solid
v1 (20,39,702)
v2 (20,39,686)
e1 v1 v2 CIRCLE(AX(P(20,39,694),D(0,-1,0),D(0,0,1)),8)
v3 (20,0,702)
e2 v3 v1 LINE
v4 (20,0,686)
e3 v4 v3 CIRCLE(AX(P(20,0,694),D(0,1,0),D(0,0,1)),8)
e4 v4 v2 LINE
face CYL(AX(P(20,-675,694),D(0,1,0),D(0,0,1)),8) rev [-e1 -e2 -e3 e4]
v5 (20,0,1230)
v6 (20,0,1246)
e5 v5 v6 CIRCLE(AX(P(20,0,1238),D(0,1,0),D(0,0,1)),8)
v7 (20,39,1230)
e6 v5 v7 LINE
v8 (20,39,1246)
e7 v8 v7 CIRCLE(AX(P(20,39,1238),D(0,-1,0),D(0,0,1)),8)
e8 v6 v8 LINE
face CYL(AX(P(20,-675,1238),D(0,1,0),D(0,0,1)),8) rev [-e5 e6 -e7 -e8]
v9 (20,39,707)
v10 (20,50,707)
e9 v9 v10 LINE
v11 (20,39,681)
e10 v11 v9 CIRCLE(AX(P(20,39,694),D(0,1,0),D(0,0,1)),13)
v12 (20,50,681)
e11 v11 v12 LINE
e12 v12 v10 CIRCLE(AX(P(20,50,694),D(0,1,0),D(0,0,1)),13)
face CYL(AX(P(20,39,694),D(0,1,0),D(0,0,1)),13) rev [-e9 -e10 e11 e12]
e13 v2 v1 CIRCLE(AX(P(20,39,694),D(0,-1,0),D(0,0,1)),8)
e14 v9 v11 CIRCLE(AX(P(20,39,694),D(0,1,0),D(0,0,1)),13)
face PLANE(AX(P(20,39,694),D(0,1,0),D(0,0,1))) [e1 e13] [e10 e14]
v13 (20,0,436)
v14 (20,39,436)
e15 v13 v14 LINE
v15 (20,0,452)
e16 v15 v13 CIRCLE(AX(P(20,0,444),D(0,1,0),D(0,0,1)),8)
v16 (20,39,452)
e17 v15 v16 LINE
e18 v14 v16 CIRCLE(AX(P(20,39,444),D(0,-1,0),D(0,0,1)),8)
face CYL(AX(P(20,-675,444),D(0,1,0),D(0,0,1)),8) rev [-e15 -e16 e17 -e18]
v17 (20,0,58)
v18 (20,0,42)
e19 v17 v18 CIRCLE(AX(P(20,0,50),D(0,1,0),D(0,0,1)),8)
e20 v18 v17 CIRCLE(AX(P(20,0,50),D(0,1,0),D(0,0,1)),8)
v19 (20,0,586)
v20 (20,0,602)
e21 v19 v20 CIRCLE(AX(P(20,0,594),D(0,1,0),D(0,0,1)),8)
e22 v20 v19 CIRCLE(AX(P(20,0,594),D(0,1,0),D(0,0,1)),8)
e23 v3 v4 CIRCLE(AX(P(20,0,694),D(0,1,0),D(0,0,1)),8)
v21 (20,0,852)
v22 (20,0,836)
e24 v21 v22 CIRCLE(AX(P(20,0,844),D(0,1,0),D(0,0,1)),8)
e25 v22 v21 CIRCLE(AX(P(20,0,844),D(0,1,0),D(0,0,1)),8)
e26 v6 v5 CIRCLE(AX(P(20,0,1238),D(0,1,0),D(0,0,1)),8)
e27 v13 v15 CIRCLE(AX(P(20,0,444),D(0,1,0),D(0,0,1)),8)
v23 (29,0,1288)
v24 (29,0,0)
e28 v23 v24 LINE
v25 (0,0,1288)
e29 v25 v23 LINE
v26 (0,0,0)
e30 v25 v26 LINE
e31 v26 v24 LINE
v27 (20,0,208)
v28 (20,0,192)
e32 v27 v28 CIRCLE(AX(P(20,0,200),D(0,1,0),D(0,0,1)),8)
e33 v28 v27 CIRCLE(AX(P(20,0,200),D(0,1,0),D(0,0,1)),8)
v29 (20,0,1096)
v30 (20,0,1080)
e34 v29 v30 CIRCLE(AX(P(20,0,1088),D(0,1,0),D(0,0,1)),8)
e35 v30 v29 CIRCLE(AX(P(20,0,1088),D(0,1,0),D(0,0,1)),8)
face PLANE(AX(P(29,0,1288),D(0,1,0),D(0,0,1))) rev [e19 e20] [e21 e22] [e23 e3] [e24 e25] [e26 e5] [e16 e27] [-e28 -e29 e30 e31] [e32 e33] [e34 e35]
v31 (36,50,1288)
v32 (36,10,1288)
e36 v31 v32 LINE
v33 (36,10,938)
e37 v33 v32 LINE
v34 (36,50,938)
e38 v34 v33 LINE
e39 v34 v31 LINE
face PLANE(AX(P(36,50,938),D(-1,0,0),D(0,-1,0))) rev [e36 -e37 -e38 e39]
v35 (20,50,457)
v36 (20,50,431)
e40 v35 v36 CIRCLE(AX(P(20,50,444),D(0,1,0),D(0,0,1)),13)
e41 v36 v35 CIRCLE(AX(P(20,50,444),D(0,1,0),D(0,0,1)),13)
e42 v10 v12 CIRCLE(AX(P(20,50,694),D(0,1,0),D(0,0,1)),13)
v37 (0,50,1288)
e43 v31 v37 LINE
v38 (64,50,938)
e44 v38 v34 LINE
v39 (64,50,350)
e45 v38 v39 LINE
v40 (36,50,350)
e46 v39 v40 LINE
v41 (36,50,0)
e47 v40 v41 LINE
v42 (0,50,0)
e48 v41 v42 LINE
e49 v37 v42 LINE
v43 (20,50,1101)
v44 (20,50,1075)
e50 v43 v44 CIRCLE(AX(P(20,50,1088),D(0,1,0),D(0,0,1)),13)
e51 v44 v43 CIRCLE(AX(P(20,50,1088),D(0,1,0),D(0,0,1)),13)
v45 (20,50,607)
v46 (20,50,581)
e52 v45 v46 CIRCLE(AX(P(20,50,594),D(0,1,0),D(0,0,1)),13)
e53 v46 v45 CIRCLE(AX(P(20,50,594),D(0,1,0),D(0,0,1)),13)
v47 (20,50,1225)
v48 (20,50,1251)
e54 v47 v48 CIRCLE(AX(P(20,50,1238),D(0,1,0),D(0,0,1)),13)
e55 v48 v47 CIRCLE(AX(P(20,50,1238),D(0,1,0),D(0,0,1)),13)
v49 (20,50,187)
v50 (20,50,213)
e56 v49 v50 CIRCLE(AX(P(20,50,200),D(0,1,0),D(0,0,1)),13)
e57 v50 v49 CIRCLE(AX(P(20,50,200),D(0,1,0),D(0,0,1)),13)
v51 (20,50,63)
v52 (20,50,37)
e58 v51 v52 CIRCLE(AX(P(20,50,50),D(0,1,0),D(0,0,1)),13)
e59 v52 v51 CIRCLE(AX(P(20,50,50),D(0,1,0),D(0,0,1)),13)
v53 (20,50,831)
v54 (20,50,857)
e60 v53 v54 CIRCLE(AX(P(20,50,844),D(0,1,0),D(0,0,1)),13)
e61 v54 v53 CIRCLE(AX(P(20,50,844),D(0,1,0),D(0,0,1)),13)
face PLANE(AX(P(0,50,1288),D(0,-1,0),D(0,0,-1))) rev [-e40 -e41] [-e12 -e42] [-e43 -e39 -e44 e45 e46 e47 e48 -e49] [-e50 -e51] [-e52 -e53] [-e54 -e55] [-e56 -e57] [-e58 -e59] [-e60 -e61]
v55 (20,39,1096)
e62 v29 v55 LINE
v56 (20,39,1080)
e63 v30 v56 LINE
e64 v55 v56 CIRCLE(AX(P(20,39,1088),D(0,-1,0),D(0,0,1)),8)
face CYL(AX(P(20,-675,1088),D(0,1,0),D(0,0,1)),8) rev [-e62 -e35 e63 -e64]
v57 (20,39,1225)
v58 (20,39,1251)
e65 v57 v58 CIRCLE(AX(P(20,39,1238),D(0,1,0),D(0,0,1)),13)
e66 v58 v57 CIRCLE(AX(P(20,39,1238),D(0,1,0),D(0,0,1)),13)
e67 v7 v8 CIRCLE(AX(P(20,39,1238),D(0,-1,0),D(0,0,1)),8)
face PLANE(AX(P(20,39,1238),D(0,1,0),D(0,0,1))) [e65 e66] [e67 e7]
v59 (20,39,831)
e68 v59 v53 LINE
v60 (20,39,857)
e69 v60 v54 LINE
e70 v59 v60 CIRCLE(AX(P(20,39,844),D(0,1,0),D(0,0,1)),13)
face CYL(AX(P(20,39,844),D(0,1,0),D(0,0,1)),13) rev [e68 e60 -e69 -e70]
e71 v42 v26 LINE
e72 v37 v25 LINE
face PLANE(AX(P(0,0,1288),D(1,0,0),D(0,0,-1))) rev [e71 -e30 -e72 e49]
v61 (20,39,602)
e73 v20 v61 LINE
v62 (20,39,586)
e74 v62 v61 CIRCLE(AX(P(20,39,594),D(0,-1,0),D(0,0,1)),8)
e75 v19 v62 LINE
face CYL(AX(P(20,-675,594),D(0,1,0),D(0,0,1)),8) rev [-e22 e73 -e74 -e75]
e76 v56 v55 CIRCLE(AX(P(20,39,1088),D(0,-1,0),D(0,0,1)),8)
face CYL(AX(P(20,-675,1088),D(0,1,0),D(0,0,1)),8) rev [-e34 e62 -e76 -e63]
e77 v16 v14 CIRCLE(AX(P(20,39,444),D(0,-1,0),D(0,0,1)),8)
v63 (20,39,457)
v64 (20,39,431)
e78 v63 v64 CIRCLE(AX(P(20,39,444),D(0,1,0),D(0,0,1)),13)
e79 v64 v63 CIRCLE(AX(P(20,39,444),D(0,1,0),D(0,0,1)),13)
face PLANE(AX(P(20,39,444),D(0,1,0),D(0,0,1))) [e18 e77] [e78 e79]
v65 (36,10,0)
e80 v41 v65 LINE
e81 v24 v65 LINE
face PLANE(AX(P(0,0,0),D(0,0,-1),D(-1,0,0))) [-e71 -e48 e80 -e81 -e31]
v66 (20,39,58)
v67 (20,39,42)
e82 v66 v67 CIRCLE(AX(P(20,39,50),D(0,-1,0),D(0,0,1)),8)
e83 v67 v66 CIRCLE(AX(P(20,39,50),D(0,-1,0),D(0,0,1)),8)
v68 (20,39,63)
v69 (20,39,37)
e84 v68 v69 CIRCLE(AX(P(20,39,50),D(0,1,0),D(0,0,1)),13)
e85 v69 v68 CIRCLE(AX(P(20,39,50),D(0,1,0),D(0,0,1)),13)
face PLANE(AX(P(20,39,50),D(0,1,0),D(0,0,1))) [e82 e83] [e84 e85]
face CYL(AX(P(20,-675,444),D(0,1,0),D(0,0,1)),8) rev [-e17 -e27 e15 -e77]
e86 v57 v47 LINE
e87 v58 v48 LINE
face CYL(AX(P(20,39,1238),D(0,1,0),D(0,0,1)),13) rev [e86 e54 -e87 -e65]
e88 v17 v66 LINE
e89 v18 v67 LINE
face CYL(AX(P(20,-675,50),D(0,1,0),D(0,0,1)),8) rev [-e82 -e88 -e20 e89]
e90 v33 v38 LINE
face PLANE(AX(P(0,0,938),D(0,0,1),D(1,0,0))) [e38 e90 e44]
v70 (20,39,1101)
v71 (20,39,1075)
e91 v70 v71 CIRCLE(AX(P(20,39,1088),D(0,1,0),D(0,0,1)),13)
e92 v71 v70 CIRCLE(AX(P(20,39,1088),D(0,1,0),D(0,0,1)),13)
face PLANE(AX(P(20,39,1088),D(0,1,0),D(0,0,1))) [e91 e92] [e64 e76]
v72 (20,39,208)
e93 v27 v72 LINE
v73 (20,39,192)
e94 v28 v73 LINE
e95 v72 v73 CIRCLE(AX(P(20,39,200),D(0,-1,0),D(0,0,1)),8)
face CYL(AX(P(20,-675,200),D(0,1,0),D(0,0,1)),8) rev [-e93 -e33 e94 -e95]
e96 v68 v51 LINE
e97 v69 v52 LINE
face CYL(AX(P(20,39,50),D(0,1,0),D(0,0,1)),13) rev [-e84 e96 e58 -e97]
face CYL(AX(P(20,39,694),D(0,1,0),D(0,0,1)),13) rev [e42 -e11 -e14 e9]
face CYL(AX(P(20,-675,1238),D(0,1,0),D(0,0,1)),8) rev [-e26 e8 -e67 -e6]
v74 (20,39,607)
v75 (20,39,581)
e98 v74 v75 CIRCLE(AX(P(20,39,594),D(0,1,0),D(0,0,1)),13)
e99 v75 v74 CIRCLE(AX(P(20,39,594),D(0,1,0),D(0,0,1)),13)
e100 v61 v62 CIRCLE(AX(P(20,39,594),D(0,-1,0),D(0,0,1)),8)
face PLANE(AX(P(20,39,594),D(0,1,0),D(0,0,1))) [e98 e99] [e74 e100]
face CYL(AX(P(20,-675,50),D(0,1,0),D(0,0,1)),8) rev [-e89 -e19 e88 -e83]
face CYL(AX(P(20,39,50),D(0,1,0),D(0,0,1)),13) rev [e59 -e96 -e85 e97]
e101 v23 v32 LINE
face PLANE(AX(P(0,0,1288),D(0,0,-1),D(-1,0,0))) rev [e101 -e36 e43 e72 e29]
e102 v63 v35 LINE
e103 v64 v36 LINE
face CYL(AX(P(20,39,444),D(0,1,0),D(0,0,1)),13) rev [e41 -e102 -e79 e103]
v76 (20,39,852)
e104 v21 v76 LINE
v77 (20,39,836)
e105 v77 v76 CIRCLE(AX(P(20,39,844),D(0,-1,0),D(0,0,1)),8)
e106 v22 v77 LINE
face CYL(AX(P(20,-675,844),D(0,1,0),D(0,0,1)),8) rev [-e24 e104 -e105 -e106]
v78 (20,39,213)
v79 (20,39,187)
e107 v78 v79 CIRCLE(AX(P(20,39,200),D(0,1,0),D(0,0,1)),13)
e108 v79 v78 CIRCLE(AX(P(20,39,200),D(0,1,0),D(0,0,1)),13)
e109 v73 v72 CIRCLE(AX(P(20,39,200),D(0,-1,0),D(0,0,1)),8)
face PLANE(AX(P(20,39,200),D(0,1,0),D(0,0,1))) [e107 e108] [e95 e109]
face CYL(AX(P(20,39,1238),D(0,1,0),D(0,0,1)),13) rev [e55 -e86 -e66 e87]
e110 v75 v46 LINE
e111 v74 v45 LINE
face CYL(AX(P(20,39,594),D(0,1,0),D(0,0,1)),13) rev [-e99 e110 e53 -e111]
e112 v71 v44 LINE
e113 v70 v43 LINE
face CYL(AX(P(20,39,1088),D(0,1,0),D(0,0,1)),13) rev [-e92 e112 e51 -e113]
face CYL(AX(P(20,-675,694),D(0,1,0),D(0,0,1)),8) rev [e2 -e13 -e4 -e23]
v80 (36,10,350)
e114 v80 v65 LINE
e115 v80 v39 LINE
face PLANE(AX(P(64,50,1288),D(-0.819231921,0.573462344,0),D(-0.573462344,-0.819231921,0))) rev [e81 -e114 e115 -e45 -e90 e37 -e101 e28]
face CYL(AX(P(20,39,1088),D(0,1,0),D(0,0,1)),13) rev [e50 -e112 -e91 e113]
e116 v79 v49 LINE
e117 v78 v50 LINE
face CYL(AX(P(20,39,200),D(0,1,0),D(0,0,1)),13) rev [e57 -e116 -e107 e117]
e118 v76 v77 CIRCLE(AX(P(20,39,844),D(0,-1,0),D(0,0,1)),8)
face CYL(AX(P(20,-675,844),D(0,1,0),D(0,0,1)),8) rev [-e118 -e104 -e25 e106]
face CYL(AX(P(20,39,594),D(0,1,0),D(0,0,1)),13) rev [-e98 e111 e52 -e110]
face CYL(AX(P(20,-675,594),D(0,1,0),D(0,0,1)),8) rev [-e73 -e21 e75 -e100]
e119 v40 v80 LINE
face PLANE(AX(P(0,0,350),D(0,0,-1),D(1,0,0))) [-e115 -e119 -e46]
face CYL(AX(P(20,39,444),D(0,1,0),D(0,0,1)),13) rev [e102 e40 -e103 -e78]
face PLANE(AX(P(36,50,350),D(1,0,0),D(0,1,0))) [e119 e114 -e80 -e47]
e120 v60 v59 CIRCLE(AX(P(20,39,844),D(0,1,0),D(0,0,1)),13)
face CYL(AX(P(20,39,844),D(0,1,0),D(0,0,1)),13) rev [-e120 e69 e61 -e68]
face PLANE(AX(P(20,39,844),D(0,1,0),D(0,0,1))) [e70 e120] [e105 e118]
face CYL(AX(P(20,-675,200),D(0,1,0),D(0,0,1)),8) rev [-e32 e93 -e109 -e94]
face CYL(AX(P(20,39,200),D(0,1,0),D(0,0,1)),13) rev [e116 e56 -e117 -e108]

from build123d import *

# Parameters (mm, degrees)
EXTRUDE_1_DEPTH     = 1288
SKETCH_2_R          = 8
CUT_EXTRUDE_1_DEPTH = 725
SKETCH_3_R          = 13
CUT_EXTRUDE_2_DEPTH = 11
CUT_EXTRUDE_3_DEPTH = 350


with BuildPart() as part:
    # 草图1 → 凸台-拉伸1 (new body)
    with BuildSketch(Plane.XY):
        Polygon((0, 0), (0, 50), (64, 50), (29, 0), align=None)
    extrude(amount=EXTRUDE_1_DEPTH)

    # 草图2 → 切除-拉伸1 (cut)
    with BuildSketch(Plane(origin=(0, 50, 0), x_dir=(1, 0, 0), z_dir=(0, 1, 0))):
        with Locations(Location((20, -50, 0), (0, 0, 270))):
            Circle(SKETCH_2_R)
        with Locations(Location((20, -200, 0), (0, 0, 270))):
            Circle(SKETCH_2_R)
        with Locations(Location((20, -444, 0), (0, 0, 270))):
            Circle(SKETCH_2_R)
        with Locations(Location((20, -594, 0), (0, 0, 270))):
            Circle(SKETCH_2_R)
        with Locations(Location((20, -694, 0), (0, 0, 270))):
            Circle(SKETCH_2_R)
        with Locations(Location((20, -844, 0), (0, 0, 270))):
            Circle(SKETCH_2_R)
        with Locations(Location((20, -1088, 0), (0, 0, 270))):
            Circle(SKETCH_2_R)
        with Locations(Location((20, -1238, 0), (0, 0, 270))):
            Circle(SKETCH_2_R)
    extrude(amount=-CUT_EXTRUDE_1_DEPTH, mode=Mode.SUBTRACT)

    # 草图3 → 切除-拉伸2 (cut)
    with BuildSketch(Plane(origin=(0, 50, 0), x_dir=(1, 0, 0), z_dir=(0, 1, 0))):
        with Locations(Location((20, -50, 0), (0, 0, 270))):
            Circle(SKETCH_3_R)
        with Locations(Location((20, -200, 0), (0, 0, 270))):
            Circle(SKETCH_3_R)
        with Locations(Location((20, -444, 0), (0, 0, 270))):
            Circle(SKETCH_3_R)
        with Locations(Location((20, -594, 0), (0, 0, 270))):
            Circle(SKETCH_3_R)
        with Locations(Location((20, -694, 0), (0, 0, 270))):
            Circle(SKETCH_3_R)
        with Locations(Location((20, -844, 0), (0, 0, 270))):
            Circle(SKETCH_3_R)
        with Locations(Location((20, -1088, 0), (0, 0, 270))):
            Circle(SKETCH_3_R)
        with Locations(Location((20, -1238, 0), (0, 0, 270))):
            Circle(SKETCH_3_R)
    extrude(amount=-CUT_EXTRUDE_2_DEPTH, mode=Mode.SUBTRACT)

    # 草图4 → 切除-拉伸3 (cut)
    with BuildSketch(Plane.XY.offset(1288)):
        Polygon((64, 50), (36, 50), (36, 10), align=None)
    cut_extrude_3 = extrude(amount=-CUT_EXTRUDE_3_DEPTH, mode=Mode.SUBTRACT)

    # 镜向1: 切除-拉伸3 across plane
    add(cut_extrude_3.mirror(Plane(origin=(0, 0, 644), x_dir=(1, 0, 0), z_dir=(0, 0, -1))), mode=Mode.SUBTRACT)


solid = part.part
